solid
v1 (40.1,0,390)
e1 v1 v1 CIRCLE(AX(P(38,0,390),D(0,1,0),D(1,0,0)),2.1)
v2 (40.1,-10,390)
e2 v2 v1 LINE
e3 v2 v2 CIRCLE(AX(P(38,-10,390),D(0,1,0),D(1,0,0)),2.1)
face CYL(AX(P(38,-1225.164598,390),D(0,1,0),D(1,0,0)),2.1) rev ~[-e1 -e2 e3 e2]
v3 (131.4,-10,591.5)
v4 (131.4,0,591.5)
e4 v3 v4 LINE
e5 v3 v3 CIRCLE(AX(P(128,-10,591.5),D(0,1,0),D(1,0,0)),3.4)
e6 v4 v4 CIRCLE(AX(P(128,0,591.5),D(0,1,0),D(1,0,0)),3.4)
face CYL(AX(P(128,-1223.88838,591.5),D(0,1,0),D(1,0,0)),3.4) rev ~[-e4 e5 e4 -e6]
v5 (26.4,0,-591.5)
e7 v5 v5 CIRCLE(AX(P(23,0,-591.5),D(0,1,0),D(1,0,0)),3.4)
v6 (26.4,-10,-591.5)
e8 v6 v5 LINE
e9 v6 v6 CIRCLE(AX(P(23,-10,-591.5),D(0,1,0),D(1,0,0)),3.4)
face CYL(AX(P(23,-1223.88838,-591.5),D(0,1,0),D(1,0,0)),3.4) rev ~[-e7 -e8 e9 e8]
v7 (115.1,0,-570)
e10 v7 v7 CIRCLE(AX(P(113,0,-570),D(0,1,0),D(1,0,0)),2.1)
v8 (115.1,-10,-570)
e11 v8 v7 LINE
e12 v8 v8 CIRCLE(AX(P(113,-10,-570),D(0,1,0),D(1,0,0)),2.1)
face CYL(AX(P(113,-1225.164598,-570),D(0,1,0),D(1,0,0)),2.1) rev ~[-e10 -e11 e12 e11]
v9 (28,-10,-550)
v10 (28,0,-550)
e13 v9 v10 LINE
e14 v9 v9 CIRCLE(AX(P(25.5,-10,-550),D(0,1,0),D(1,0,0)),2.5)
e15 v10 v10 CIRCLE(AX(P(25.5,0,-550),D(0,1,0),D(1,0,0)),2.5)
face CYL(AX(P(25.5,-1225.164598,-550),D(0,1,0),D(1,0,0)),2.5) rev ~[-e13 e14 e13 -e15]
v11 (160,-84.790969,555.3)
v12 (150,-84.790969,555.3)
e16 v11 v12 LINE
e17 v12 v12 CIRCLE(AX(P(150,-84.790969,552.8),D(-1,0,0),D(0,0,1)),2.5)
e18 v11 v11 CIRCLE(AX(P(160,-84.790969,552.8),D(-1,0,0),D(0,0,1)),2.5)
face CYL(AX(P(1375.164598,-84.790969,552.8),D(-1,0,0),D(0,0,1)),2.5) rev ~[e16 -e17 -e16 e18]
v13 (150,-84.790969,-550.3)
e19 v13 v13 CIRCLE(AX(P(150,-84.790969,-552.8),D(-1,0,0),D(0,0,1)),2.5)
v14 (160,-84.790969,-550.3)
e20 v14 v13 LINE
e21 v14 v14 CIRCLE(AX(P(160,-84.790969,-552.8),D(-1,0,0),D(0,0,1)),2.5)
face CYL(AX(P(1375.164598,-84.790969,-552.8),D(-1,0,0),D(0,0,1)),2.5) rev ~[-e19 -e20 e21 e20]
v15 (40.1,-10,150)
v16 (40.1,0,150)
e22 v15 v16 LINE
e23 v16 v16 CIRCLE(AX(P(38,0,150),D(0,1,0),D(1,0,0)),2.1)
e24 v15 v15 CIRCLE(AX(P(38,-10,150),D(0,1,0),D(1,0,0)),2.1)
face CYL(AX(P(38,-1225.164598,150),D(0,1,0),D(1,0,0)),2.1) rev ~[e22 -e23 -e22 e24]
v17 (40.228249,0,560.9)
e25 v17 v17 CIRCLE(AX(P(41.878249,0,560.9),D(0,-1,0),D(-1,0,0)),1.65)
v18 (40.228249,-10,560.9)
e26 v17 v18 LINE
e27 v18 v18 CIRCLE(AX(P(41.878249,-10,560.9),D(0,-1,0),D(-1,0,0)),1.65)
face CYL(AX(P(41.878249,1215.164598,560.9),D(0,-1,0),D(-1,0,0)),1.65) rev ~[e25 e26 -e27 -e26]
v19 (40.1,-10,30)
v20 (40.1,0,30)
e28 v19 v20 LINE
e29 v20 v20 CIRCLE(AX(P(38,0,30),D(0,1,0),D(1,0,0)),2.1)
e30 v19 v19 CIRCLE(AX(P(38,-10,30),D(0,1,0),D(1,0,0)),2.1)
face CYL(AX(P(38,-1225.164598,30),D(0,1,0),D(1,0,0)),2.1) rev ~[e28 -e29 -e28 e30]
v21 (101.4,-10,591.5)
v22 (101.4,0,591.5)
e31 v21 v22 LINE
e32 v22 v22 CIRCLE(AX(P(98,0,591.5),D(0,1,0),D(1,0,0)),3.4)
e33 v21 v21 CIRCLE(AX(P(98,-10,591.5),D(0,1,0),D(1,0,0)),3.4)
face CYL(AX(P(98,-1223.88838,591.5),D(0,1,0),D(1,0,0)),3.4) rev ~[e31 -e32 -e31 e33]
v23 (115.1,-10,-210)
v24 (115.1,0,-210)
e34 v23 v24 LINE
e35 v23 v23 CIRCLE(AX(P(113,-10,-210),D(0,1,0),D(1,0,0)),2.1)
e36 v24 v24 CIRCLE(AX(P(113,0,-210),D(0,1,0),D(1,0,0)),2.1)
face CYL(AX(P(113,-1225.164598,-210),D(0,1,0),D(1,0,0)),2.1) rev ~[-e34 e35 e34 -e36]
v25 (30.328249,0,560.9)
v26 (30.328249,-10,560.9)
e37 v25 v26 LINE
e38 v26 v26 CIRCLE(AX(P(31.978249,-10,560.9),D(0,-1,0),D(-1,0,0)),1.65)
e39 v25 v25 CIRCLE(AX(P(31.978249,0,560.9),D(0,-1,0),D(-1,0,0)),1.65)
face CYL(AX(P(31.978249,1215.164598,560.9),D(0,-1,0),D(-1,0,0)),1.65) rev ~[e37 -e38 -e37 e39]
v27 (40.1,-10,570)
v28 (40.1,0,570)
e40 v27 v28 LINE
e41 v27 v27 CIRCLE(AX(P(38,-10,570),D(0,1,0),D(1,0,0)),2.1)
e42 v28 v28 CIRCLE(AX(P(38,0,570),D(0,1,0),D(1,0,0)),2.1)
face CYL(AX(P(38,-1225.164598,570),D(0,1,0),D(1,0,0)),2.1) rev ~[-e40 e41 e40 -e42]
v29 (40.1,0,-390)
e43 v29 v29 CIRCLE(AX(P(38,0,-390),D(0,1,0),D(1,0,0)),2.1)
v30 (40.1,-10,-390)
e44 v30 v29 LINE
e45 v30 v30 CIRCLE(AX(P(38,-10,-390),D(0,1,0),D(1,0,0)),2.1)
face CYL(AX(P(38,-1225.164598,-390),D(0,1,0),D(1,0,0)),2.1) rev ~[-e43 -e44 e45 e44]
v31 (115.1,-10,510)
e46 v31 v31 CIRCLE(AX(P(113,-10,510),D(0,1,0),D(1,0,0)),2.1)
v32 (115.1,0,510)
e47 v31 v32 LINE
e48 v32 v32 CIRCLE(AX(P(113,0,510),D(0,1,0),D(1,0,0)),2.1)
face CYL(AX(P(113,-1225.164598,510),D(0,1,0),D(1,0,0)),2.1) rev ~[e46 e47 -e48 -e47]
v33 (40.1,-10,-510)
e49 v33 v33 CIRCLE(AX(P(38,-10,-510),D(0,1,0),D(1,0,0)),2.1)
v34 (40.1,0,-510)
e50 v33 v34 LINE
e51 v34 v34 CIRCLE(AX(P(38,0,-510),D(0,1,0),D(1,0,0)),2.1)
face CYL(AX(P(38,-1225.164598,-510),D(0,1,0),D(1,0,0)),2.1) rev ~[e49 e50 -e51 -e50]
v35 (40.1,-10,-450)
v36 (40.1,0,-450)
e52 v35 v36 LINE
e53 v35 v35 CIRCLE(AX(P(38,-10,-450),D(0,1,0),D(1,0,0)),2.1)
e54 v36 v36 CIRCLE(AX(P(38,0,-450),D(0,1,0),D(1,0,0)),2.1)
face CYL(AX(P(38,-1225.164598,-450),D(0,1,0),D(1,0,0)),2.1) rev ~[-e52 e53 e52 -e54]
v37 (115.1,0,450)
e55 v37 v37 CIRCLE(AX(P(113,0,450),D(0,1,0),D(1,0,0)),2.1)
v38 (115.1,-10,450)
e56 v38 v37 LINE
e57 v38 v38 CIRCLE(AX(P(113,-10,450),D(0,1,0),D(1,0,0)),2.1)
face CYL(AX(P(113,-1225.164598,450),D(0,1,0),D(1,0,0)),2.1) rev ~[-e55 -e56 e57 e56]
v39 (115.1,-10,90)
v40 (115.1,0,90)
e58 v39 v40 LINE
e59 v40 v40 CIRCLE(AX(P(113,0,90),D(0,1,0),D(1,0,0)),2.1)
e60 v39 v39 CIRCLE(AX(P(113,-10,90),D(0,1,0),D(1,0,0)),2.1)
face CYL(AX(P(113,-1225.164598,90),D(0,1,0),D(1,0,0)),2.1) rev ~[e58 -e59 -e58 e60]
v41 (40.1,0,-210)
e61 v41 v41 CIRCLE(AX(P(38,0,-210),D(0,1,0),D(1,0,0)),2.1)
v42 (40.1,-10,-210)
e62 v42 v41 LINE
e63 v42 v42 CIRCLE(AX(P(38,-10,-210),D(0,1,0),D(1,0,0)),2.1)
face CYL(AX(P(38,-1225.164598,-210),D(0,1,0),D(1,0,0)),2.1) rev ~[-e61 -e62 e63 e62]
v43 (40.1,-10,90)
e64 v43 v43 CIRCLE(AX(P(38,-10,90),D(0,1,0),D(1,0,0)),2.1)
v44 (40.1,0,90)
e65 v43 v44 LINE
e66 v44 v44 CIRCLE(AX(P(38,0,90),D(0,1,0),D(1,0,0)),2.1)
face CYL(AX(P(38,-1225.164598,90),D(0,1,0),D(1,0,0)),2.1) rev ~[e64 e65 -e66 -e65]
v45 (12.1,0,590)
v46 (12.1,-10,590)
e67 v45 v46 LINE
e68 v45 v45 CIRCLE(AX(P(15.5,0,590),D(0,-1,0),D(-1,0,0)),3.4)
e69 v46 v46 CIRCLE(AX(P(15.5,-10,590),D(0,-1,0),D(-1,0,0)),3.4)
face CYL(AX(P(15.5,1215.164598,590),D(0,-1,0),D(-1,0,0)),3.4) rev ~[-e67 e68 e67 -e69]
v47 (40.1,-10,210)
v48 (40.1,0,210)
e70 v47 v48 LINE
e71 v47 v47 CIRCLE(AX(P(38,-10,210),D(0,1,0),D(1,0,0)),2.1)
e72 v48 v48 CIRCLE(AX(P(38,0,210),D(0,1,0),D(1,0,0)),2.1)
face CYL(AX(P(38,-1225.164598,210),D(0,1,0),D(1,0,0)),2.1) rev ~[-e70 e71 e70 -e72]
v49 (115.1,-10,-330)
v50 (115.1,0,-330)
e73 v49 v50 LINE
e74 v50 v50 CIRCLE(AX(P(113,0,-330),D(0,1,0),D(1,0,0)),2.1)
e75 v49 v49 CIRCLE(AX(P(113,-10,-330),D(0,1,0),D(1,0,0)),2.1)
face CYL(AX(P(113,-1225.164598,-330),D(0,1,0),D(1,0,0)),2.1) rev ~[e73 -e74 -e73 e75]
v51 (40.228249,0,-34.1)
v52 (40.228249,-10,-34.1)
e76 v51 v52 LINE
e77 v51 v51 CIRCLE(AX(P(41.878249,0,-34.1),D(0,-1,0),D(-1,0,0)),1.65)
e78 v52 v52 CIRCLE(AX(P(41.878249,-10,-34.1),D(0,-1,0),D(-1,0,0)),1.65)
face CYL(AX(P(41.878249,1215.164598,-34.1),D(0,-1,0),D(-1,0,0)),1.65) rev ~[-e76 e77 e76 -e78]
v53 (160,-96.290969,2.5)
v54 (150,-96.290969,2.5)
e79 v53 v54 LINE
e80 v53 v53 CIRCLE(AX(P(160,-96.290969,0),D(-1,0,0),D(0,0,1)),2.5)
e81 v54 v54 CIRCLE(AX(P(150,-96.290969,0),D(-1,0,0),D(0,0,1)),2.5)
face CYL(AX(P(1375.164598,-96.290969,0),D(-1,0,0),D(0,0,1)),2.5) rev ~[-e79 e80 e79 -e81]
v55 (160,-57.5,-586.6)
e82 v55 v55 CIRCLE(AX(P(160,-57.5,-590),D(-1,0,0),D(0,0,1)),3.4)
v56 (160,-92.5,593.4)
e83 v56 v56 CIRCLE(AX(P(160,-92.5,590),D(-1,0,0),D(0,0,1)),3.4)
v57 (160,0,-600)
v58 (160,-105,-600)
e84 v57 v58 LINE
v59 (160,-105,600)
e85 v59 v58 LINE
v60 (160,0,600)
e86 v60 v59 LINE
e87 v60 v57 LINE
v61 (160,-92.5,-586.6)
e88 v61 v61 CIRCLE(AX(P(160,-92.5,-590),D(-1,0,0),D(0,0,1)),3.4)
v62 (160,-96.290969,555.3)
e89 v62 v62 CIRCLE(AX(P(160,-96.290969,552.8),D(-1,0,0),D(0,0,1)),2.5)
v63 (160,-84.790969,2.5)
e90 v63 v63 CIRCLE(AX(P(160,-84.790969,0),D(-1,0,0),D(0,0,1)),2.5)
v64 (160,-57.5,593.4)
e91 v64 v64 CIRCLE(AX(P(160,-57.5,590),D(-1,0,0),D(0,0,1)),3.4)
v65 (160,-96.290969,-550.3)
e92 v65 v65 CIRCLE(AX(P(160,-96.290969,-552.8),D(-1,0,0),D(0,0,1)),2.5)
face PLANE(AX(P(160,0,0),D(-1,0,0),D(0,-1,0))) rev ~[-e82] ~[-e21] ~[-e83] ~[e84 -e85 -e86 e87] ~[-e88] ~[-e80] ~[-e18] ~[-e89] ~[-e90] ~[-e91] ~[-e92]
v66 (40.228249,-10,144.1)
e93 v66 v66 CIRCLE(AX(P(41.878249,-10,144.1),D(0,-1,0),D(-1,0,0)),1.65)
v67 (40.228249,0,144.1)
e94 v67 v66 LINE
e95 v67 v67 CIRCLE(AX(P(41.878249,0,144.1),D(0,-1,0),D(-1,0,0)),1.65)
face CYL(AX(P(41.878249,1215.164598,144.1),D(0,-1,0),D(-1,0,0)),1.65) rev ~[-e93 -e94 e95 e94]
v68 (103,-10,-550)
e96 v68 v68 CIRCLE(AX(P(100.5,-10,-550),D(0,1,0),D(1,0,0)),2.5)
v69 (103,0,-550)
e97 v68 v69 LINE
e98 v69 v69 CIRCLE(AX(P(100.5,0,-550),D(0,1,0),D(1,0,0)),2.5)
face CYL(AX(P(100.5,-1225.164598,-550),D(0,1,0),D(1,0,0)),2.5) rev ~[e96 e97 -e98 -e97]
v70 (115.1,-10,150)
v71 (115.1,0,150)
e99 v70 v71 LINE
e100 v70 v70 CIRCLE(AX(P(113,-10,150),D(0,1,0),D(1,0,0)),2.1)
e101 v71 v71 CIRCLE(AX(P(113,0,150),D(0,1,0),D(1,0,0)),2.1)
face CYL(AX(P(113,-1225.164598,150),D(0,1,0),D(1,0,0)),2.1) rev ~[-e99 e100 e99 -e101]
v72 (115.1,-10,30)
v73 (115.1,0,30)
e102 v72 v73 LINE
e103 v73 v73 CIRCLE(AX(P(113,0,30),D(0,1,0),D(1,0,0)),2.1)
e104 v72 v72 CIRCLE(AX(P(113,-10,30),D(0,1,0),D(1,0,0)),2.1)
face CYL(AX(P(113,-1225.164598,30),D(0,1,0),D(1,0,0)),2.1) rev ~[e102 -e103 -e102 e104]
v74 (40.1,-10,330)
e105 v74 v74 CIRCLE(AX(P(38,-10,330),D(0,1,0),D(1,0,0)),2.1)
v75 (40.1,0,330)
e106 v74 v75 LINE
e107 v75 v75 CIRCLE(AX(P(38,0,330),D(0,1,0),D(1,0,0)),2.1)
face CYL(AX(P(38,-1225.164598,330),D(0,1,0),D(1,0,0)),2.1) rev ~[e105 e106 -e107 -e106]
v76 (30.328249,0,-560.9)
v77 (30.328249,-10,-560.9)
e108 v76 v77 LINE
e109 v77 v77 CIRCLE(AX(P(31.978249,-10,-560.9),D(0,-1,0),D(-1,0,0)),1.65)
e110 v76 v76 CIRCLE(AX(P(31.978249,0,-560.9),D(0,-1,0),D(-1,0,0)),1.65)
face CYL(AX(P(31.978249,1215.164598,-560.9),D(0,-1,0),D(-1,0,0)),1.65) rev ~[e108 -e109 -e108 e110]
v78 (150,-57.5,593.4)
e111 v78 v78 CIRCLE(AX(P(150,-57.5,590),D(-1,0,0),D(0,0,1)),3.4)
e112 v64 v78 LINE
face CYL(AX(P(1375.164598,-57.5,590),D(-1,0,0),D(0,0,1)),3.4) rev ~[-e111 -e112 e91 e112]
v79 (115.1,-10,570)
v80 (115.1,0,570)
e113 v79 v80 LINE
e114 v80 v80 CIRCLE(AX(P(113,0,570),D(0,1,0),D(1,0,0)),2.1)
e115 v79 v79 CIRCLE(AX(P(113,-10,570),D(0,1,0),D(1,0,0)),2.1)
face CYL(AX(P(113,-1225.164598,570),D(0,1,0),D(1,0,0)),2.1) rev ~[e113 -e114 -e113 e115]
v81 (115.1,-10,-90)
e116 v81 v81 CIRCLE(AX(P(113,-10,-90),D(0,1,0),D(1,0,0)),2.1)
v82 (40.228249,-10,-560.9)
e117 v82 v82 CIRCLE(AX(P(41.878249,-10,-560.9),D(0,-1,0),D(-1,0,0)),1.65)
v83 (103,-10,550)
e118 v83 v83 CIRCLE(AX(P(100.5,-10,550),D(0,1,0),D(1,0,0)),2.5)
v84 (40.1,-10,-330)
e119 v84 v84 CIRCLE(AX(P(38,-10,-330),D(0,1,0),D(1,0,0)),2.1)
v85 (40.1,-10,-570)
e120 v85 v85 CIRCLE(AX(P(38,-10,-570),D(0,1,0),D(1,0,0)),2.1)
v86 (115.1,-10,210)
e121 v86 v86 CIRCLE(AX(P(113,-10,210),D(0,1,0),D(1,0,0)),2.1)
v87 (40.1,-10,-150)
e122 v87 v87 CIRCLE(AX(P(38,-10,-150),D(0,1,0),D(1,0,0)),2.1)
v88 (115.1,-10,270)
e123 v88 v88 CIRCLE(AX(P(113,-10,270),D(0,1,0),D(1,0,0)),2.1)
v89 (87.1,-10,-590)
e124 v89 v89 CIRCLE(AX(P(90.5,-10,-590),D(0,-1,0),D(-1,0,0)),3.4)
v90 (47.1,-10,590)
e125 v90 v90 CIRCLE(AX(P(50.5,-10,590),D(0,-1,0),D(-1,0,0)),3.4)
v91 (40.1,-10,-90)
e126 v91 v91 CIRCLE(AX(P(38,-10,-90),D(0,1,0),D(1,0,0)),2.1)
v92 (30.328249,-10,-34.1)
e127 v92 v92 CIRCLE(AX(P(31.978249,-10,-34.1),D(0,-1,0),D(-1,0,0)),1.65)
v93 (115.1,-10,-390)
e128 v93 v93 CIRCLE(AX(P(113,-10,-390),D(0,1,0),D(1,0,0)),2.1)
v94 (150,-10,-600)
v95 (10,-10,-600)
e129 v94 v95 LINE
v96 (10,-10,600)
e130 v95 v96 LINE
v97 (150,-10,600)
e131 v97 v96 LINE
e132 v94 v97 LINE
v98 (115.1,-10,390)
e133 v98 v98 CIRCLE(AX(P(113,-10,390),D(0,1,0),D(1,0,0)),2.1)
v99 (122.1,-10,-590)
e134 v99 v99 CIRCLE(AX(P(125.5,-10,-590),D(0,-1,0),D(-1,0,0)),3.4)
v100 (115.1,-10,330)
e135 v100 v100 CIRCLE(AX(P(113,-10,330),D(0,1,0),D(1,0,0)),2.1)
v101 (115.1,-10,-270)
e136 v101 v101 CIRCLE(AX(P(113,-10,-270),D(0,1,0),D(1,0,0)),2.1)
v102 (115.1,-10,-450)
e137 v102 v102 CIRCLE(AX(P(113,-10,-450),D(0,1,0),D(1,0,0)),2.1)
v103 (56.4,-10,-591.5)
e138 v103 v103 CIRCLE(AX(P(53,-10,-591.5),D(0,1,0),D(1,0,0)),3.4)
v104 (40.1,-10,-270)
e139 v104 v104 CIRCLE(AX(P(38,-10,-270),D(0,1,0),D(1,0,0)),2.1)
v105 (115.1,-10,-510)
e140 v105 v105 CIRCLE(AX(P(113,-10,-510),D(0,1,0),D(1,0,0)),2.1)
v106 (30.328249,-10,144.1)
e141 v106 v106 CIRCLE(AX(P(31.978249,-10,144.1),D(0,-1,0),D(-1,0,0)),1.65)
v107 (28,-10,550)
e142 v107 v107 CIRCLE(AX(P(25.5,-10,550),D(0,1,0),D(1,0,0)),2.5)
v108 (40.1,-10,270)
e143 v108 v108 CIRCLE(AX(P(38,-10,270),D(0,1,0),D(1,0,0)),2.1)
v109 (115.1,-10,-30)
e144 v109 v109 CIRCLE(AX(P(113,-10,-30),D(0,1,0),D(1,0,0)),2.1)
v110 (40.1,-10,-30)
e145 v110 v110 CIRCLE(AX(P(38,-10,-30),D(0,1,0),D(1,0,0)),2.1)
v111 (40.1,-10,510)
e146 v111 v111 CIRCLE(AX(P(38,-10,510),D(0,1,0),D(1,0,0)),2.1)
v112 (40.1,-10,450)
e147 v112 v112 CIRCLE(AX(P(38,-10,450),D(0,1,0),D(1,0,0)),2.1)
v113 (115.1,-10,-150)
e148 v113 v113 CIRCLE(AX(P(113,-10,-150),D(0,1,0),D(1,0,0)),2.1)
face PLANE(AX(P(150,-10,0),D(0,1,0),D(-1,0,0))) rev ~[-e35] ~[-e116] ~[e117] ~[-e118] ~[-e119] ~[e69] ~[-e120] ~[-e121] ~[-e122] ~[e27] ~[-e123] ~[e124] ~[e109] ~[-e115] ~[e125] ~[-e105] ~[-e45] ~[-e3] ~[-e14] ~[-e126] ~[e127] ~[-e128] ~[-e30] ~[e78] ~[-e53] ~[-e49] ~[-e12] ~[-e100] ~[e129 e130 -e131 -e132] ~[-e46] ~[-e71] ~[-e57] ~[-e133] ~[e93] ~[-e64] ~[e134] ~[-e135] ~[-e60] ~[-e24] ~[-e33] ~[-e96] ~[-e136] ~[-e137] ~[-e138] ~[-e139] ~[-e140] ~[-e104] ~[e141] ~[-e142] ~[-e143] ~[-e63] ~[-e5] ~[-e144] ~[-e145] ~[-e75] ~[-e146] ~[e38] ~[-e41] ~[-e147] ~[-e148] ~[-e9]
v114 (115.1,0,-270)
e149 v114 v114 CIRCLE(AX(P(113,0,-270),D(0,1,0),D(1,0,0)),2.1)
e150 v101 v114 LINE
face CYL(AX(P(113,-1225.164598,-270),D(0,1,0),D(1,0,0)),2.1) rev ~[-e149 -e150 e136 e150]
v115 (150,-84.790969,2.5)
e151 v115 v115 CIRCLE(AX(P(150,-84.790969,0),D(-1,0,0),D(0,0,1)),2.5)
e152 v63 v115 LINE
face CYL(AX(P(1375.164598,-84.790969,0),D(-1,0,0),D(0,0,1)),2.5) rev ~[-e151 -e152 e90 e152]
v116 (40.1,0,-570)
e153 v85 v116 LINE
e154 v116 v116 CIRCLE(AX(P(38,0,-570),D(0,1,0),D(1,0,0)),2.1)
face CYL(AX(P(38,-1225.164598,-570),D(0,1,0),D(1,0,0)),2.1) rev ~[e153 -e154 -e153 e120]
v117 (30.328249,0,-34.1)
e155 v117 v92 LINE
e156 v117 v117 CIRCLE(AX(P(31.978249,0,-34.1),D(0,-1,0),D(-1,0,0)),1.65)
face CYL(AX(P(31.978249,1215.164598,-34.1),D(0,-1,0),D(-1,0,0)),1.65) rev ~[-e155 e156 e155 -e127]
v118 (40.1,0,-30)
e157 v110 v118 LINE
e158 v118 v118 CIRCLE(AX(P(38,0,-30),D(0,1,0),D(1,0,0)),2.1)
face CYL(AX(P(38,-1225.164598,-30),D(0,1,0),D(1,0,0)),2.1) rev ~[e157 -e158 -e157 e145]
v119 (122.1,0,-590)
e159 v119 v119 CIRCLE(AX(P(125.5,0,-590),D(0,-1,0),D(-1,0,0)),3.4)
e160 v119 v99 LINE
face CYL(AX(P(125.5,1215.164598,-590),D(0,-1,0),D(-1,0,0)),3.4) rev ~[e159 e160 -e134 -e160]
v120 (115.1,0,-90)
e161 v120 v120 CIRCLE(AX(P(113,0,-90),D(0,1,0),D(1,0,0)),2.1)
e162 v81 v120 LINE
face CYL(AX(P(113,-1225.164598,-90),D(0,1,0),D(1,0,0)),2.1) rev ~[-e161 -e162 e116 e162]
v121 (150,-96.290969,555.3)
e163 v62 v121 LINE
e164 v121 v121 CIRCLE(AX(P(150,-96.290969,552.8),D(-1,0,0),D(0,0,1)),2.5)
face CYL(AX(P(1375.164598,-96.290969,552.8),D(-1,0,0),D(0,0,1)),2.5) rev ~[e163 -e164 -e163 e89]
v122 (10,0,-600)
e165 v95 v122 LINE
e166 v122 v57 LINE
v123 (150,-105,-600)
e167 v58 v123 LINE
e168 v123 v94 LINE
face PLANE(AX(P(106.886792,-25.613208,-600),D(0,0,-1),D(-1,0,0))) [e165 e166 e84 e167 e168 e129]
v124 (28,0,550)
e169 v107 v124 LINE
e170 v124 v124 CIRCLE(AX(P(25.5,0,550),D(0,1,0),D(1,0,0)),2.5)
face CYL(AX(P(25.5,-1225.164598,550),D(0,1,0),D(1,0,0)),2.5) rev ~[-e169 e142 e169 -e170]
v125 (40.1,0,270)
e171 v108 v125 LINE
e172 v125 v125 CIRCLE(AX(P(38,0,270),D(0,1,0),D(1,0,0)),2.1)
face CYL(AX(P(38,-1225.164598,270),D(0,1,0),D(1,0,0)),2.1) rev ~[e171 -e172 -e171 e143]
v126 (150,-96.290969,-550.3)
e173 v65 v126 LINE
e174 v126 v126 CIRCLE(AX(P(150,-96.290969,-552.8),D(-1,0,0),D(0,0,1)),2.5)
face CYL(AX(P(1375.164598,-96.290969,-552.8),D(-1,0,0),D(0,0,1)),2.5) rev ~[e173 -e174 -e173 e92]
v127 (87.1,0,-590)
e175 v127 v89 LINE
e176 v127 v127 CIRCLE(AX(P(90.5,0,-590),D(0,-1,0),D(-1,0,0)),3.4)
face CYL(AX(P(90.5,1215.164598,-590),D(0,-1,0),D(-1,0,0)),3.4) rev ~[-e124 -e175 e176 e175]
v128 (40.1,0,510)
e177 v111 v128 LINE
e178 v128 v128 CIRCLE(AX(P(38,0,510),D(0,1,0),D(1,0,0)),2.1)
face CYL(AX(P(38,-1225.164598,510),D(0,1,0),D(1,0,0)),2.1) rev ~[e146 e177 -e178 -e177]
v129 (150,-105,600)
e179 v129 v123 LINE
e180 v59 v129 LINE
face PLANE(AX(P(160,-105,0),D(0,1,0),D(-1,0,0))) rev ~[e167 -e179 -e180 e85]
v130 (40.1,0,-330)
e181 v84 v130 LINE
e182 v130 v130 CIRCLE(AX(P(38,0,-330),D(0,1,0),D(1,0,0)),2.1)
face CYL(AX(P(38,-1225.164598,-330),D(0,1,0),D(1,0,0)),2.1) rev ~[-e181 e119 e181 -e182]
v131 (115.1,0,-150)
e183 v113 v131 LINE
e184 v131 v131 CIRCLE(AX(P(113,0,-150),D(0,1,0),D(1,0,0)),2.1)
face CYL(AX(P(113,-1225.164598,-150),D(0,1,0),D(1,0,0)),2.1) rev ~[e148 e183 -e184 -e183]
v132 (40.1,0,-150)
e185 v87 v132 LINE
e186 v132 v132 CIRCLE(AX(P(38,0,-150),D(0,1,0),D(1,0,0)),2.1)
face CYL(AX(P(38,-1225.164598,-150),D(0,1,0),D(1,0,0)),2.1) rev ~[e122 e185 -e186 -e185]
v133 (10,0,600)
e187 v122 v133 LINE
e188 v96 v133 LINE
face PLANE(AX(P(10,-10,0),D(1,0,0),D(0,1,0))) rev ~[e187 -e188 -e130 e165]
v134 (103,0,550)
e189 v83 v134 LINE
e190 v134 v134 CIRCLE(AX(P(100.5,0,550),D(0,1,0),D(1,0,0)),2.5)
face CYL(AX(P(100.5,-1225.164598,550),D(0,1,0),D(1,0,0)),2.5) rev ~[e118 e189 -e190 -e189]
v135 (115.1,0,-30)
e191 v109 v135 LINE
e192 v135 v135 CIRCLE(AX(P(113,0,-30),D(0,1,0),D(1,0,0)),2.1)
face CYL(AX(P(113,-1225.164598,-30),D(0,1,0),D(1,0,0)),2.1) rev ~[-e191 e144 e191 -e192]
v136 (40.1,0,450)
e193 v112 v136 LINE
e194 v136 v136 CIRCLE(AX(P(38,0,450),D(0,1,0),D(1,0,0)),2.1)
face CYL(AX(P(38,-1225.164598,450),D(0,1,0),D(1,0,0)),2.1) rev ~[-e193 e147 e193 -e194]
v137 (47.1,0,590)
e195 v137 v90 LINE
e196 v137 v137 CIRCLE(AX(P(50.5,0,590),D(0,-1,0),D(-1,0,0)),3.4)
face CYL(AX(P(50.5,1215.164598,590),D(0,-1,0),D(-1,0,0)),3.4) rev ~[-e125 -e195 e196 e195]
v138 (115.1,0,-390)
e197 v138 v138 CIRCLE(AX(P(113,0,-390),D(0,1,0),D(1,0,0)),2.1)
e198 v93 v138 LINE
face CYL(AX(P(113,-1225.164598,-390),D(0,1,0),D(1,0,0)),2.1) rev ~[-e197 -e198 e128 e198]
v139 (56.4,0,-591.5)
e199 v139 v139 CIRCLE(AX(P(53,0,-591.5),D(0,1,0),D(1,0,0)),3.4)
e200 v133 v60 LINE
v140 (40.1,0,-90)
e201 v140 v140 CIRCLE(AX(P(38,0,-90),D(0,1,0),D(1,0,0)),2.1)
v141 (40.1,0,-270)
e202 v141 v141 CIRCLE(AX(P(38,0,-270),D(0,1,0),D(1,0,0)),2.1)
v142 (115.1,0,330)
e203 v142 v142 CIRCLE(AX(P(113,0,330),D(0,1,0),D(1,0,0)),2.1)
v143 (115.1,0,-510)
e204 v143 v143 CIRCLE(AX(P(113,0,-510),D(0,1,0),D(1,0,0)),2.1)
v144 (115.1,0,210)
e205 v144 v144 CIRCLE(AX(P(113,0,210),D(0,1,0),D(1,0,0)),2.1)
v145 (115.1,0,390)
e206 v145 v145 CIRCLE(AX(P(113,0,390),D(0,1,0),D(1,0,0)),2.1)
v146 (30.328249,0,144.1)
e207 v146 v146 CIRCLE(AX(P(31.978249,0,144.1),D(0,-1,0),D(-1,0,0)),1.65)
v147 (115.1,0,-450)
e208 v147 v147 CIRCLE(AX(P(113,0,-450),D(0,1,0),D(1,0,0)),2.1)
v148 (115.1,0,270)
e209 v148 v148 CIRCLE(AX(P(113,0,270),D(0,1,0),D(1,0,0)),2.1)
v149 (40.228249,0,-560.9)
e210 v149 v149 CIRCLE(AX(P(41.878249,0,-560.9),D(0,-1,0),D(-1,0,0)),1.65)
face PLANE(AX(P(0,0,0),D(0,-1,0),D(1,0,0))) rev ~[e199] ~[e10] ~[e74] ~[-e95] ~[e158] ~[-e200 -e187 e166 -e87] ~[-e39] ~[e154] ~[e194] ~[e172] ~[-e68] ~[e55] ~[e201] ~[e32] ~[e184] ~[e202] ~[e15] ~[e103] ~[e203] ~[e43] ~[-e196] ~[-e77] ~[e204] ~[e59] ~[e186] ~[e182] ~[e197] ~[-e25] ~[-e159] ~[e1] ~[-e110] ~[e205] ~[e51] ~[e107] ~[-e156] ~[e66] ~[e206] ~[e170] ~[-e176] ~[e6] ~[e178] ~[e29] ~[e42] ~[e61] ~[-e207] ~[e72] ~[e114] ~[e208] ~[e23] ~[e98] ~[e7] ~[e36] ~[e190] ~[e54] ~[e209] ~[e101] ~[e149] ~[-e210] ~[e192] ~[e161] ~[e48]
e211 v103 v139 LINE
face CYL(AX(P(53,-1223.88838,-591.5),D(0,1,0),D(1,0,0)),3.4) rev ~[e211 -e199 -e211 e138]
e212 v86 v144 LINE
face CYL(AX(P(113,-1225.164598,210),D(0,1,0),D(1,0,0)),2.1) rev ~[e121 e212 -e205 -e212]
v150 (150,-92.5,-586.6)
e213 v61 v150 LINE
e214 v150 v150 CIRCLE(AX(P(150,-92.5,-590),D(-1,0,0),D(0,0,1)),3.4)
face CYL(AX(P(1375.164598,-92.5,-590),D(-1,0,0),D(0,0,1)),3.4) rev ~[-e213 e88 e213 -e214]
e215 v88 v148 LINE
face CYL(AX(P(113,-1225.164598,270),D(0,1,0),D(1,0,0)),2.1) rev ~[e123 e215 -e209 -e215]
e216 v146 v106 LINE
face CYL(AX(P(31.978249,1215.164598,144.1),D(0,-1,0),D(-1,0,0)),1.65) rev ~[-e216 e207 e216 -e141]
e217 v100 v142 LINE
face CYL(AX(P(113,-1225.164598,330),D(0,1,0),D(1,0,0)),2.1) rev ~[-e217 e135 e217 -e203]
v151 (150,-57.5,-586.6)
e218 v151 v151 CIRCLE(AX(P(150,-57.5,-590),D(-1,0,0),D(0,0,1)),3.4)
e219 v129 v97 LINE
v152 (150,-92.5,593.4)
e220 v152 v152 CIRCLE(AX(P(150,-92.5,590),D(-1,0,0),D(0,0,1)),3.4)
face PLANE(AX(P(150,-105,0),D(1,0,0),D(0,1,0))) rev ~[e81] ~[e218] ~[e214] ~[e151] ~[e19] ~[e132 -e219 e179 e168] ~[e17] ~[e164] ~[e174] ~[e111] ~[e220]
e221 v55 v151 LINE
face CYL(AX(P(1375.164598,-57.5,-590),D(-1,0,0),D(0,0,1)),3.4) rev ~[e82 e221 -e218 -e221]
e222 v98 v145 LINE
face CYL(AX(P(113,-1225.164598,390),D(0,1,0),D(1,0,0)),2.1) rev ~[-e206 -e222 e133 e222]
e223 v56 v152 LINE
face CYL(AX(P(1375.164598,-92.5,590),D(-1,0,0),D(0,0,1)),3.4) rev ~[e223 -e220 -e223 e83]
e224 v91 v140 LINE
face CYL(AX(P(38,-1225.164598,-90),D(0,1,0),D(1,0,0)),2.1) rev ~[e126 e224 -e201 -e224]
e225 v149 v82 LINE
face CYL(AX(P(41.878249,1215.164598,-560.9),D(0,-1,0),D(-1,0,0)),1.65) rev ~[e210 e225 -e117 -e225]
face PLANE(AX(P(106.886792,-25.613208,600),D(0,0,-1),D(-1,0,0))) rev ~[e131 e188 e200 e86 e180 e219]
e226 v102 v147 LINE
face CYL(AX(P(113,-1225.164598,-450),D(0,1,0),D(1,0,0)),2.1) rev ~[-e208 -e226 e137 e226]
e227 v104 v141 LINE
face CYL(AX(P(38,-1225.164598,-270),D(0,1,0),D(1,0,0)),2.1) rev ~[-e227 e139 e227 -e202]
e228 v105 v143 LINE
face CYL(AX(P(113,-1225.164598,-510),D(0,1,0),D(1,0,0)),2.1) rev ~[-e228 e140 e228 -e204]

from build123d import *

# Parameters (mm, degrees)
EXTRUDE_1_DEPTH    = 600
HOLE_WIZARD_M8_1_D = 6.8
HOLE_WIZARD_M8_2_D = 6.8
HOLE_WIZARD_M5_1_D = 4.2
F_5_0MM_1_D        = 5
HOLE_WIZARD_M4_1_D = 3.3
HOLE_WIZARD_M6_1_D = 5
MOVE_FACE_1_BY     = 10
HOLE_WIZARD_M8_3_D = 6.8


with BuildPart() as part:
    # 草图1 → 凸台-拉伸1 (new, symmetric)
    with BuildSketch(Plane.XY):
        Polygon((0, 0), (160, 0), (160, -105), (150, -105), (150, -10), (0, -10), align=None)
    extrude(amount=EXTRUDE_1_DEPTH, both=True)

    # M8 螺纹孔1 (through all)
    with Locations(Plane(origin=(0, 0, 0), x_dir=(1, 0, 0), z_dir=(0, 1, 0))):
        with Locations((15.5, -590), (50.5, -590), (90.5, 590), (125.5, 590)):
            Hole(HOLE_WIZARD_M8_1_D / 2)

    # M8 螺纹孔2 (through all)
    with Locations(Plane(origin=(160, 0, 0), x_dir=(0, 0, -1), z_dir=(1, 0, 0))):
        with Locations((-590, -57.5), (-590, -92.5), (590, -92.5), (590, -57.5)):
            Hole(HOLE_WIZARD_M8_2_D / 2)

    # M5 螺纹孔1 (through all)
    with Locations(Plane(origin=(0, -10, 0), x_dir=(-1, 0, 0), z_dir=(0, -1, 0))):
        with Locations((-38, -570), (-38, -510), (-38, -450), (-38, -390), (-38, -330), (-38, -270), (-38, -210), (-38, -150), (-38, -90), (-38, -30), (-38, 30), (-38, 90), (-38, 150), (-38, 210), (-38, 270), (-38, 330), (-38, 390), (-38, 450), (-38, 510), (-38, 570), (-113, -570), (-113, -510), (-113, -450), (-113, -390), (-113, -330), (-113, -270), (-113, -210), (-113, -150), (-113, -90), (-113, -30), (-113, 30), (-113, 90), (-113, 150), (-113, 210), (-113, 270), (-113, 330), (-113, 390), (-113, 450), (-113, 510), (-113, 570)):
            Hole(HOLE_WIZARD_M5_1_D / 2)

    # Ø5.0mm 暗销孔1 (through all)
    with Locations(Plane(origin=(0, -10, 0), x_dir=(-1, 0, 0), z_dir=(0, -1, 0))):
        with Locations((-25.5, 550), (-25.5, -550), (-100.5, 550), (-100.5, -550)):
            Hole(F_5_0MM_1_D / 2)

    # M4 螺纹孔1 (through all)
    with Locations(Plane(origin=(0, 0, 0), x_dir=(1, 0, 0), z_dir=(0, 1, 0))):
        with Locations((31.978248954, 560.9), (41.878248954, 560.9), (31.978248954, 34.1), (41.878248954, 34.1), (31.978248954, -144.1), (41.878248954, -144.1), (31.978248954, -560.9), (41.878248954, -560.9)):
            Hole(HOLE_WIZARD_M4_1_D / 2)

    # M6 螺纹孔1 (through all)
    with Locations(Plane(origin=(160, 0, 0), x_dir=(0, 0, -1), z_dir=(1, 0, 0))):
        with Locations((-552.8, -84.790968568), (-552.8, -96.290968568), (0, -84.790968568), (0, -96.290968568), (552.8, -84.790968568), (552.8, -96.290968568)):
            Hole(HOLE_WIZARD_M6_1_D / 2)

    # Move Face 1: a face moved inward by 10.0
    extrude(part.faces().sort_by_distance((0, -5, 0))[0], amount=MOVE_FACE_1_BY, dir=(1, 0, 0), mode=Mode.SUBTRACT)

    # M8 螺纹孔3 (through all)
    with Locations(Plane(origin=(0, -10, 0), x_dir=(-1, 0, 0), z_dir=(0, -1, 0))):
        with Locations((-53, 591.5), (-23, 591.5), (-128.000000121, -591.5), (-97.999999879, -591.5)):
            Hole(HOLE_WIZARD_M8_3_D / 2)


solid = part.part
